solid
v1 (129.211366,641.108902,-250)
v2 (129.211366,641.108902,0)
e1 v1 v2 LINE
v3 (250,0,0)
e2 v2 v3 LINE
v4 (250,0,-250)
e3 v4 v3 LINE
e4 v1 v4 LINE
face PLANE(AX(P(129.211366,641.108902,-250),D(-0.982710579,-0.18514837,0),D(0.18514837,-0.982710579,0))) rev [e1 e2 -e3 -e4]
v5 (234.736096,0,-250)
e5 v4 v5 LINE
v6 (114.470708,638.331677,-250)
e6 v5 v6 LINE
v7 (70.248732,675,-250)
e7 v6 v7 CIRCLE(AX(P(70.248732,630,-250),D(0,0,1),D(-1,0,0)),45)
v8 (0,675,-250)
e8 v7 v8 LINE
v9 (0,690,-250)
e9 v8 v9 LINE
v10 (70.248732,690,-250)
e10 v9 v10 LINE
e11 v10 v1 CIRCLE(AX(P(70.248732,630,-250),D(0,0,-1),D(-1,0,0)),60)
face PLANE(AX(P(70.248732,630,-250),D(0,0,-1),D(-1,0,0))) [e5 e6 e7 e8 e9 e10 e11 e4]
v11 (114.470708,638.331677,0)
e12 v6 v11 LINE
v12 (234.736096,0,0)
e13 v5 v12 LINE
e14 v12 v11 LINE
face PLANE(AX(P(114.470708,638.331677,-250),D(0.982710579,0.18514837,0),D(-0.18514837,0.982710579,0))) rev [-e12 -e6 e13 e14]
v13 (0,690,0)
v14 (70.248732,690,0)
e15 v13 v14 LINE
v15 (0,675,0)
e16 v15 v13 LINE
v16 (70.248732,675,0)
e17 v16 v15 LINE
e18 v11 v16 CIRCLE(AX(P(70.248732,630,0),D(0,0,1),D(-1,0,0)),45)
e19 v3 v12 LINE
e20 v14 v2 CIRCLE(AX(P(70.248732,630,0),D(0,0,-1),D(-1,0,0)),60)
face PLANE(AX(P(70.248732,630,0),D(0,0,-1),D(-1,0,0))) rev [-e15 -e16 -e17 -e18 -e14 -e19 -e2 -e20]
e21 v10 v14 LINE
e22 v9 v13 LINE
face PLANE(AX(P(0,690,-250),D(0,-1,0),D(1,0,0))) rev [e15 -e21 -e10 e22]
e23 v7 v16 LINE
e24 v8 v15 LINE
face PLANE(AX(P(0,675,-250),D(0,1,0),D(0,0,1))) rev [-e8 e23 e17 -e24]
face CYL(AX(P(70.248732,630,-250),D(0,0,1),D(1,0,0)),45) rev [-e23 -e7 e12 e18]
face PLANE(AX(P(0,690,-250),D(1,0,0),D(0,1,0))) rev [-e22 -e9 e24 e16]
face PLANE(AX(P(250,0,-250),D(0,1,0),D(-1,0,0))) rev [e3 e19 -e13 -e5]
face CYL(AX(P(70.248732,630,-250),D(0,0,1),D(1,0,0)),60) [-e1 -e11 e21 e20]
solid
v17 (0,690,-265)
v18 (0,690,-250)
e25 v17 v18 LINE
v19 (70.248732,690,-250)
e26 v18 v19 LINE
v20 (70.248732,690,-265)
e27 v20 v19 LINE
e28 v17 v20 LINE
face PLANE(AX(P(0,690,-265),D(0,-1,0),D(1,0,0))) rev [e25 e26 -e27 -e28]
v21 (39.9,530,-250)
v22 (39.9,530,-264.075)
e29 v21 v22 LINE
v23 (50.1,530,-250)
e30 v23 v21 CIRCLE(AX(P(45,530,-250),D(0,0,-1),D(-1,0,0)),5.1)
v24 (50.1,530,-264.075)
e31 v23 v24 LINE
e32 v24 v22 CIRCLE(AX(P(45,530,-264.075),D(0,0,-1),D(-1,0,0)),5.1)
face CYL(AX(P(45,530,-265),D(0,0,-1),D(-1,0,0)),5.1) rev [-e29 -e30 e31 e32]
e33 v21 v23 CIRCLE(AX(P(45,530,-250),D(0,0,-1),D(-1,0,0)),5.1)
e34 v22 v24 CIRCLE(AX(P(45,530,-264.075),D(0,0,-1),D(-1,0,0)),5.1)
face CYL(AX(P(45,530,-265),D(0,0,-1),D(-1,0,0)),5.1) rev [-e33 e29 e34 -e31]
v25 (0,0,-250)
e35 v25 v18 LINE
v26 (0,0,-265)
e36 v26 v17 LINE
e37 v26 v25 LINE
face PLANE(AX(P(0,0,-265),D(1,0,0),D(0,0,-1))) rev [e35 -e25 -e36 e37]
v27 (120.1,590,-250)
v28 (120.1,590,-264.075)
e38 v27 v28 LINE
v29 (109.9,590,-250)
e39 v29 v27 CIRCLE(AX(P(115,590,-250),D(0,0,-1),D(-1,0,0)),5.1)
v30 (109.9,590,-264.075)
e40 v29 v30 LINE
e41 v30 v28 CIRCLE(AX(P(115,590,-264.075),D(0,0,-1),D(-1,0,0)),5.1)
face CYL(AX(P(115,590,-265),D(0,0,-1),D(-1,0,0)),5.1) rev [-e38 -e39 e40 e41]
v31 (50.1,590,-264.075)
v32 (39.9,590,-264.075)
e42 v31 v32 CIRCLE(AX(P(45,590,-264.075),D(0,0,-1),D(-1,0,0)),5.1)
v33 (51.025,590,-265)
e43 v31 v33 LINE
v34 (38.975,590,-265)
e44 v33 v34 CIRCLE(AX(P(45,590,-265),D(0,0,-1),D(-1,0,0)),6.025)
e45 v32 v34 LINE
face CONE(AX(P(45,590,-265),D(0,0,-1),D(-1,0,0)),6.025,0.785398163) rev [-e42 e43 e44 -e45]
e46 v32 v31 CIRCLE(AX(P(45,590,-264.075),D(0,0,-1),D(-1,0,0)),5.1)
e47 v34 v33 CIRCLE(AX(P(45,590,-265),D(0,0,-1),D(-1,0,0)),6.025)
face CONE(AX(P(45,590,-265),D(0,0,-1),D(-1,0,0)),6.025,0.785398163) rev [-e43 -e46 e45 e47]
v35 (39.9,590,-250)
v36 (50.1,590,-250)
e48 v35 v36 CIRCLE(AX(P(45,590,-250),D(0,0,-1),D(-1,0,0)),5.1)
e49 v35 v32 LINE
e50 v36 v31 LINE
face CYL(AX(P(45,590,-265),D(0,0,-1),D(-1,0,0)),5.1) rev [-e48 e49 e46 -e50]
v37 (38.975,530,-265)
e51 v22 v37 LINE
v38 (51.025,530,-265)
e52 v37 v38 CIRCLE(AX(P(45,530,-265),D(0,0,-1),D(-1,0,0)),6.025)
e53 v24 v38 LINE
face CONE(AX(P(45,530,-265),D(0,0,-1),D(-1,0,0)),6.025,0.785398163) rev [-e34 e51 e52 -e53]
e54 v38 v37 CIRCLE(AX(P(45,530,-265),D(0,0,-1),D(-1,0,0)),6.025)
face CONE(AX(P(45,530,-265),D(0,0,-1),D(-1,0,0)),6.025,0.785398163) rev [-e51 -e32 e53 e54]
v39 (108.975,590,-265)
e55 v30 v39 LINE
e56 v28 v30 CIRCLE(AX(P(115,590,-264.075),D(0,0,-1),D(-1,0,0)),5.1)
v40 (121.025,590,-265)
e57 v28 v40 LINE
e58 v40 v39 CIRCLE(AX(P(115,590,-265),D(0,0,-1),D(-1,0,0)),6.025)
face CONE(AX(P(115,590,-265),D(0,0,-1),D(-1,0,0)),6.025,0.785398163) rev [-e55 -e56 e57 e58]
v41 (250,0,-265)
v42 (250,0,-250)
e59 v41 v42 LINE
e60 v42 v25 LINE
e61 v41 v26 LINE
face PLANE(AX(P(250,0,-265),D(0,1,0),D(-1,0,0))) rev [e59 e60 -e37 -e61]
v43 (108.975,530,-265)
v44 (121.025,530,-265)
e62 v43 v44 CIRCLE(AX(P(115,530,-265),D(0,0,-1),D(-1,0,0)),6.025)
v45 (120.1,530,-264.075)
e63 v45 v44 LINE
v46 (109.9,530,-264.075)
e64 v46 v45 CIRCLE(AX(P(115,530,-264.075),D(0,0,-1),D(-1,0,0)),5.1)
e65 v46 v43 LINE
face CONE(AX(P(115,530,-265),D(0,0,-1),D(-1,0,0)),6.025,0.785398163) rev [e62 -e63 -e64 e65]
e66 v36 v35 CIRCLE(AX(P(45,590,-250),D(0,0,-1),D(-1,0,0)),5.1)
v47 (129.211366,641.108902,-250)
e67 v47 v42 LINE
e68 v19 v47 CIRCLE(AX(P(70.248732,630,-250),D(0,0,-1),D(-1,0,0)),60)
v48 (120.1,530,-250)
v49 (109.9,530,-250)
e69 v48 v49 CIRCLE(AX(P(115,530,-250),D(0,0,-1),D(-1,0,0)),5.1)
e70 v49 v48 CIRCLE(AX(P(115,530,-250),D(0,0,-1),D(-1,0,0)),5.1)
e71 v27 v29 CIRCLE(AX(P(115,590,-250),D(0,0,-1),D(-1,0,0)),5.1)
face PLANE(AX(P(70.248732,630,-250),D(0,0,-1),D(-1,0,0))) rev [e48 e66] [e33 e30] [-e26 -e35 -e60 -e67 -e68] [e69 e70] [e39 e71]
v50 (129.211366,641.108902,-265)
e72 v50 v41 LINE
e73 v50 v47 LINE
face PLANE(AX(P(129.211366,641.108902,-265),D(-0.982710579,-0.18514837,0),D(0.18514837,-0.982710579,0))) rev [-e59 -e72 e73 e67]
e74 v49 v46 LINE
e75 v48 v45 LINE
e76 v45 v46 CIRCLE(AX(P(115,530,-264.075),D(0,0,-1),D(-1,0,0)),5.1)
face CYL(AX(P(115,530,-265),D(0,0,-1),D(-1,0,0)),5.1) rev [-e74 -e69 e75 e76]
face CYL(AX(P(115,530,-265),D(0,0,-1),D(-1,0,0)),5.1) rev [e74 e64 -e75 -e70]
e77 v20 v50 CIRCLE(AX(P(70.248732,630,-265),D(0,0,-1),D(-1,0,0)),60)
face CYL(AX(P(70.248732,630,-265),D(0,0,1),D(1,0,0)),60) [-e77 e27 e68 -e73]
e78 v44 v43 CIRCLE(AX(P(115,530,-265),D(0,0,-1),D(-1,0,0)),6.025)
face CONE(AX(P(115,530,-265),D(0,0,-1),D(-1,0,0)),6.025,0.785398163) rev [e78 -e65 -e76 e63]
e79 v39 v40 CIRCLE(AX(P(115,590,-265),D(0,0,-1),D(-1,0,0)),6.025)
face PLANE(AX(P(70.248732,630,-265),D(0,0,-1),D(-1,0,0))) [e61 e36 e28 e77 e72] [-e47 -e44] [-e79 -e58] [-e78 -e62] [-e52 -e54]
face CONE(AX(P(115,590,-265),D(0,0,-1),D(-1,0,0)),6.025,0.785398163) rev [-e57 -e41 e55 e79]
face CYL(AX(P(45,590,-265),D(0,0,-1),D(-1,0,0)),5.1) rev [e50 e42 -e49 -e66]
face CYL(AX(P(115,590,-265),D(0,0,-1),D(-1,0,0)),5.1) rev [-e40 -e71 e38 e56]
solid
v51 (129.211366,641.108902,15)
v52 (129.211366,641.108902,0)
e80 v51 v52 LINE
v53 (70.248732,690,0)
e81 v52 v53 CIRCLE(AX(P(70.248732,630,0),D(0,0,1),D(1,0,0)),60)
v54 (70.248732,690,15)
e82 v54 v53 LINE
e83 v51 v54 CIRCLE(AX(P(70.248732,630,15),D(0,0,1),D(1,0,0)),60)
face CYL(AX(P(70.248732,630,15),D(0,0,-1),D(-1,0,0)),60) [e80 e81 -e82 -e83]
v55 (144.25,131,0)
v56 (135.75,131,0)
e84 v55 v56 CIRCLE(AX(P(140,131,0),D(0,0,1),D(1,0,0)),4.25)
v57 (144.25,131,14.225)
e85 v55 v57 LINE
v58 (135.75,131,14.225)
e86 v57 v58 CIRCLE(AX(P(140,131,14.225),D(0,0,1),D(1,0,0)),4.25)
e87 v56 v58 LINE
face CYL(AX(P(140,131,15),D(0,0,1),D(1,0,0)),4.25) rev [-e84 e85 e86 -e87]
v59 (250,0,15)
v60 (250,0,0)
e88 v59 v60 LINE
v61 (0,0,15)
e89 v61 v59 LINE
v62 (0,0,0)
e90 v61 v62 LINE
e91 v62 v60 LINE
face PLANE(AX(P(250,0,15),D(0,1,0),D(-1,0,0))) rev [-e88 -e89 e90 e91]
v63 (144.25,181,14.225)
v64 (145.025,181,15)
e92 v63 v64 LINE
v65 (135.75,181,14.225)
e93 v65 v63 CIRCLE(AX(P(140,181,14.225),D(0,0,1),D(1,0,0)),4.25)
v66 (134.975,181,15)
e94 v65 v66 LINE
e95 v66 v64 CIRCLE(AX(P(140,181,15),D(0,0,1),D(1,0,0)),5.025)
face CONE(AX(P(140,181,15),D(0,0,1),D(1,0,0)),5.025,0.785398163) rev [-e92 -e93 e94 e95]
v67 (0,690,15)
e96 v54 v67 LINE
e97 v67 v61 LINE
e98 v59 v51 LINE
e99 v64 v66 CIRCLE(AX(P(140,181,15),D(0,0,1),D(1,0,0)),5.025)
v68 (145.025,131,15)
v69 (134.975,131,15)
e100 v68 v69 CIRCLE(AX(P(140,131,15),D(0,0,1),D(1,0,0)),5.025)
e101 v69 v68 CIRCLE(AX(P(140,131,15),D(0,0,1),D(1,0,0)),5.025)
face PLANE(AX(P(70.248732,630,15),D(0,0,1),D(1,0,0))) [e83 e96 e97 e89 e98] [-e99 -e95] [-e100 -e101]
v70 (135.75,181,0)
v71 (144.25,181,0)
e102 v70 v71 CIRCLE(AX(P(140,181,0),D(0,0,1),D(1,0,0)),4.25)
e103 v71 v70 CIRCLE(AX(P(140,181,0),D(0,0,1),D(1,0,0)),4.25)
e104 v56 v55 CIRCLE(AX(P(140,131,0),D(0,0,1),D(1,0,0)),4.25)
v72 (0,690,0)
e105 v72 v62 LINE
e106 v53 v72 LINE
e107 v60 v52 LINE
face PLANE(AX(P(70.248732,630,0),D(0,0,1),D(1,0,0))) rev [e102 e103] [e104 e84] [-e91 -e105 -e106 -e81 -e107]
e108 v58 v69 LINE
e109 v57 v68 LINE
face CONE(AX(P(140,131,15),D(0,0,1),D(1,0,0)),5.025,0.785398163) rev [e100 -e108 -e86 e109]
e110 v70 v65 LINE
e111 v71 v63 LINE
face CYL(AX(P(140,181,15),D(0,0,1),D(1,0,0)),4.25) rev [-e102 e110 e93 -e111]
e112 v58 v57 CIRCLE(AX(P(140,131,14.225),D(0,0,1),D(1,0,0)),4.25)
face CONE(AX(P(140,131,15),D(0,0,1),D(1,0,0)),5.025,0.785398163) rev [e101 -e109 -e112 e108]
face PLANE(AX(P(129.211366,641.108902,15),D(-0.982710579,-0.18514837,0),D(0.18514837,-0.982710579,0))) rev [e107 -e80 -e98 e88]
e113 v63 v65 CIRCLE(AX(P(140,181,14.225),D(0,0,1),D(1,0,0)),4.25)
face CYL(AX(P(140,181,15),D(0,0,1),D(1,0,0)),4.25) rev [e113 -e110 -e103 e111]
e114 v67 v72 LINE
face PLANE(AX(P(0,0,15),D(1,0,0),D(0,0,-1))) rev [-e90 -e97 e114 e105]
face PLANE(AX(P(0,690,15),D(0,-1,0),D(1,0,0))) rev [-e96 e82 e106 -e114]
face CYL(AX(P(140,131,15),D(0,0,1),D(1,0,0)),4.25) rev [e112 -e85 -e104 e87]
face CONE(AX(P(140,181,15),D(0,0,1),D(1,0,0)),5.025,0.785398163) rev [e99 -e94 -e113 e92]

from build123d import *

# Parameters (mm, degrees)
EXTRUDE_1_DEPTH              = 15
EXTRUDE_2_DEPTH              = 250
EXTRUDE_3_DEPTH              = 15
HOLE_WIZARD_M10_1_AT_2_COUNT = 2
HOLE_WIZARD_M10_1_AT_2_PITCH = 50
HOLE_WIZARD_M12_1_AT_2_COUNT = 2
HOLE_WIZARD_M12_1_AT_2_PITCH = 70
HOLE_WIZARD_M12_1_AT_3_COUNT = 2
HOLE_WIZARD_M12_1_AT_3_PITCH = 92.195444573
HOLE_WIZARD_M12_1_AT_4_COUNT = 2
HOLE_WIZARD_M12_1_AT_4_PITCH = 60


with BuildPart() as part:
    # 草图1 → 凸台-拉伸1 (new body)
    with BuildSketch(Plane.XY):
        with BuildLine():
            Line((0, 0), (0, 690))
            Line((0, 690), (70.248731542, 690))
            ThreePointArc((70.248731542, 690), (108.546681021, 676.187304162), (129.211366254, 641.108902192))
            Line((129.211366254, 641.108902192), (250, 0))
            Line((250, 0), (0, 0))
        make_face()
    extrude(amount=EXTRUDE_1_DEPTH)

    # 草图5 → M10 螺纹孔1 (revolve, cut)
    with BuildSketch(Plane(origin=(140, 181, 15), x_dir=(0, -1, 0), z_dir=(1, 0, 0))):
        Polygon((0, 0), (0, 15), (4.25, 15), (4.25, 0.775), (5.025, 0), align=None)
    hole_wizard_m10_1 = revolve(axis=Axis((140, 181, 21.35), (0, 0, -1)), mode=Mode.SUBTRACT)

    # M10 螺纹孔1 at 2: M10 螺纹孔1 ×2
    with Locations(*[(0, -i * HOLE_WIZARD_M10_1_AT_2_PITCH, 0) for i in range(1, HOLE_WIZARD_M10_1_AT_2_COUNT)]):
        add(hole_wizard_m10_1, mode=Mode.SUBTRACT)


with BuildPart() as body_2:
    # 草图2 → 凸台-拉伸2 (new body)
    with BuildSketch(Plane(origin=(0, 0, 0), x_dir=(-1, 0, 0), z_dir=(0, 0, -1))):
        with BuildLine():
            Line((0, 675), (-70.248731542, 675))
            ThreePointArc((-70.248731542, 675), (-98.972193651, 664.640478122), (-114.470707576, 638.331676644))
            Line((-114.470707576, 638.331676644), (-234.736095929, 0))
            Line((-234.736095929, 0), (-250, 0))
            Line((-250, 0), (-129.211366254, 641.108902192))
            ThreePointArc((-129.211366254, 641.108902192), (-108.546681021, 676.187304162), (-70.248731542, 690))
            Line((-70.248731542, 690), (0, 690))
            Line((0, 690), (0, 675))
        make_face()
    extrude(amount=EXTRUDE_2_DEPTH)


with BuildPart() as body_3:
    # 草图3 → 凸台-拉伸3 (new body)
    with BuildSketch(Plane(origin=(0, 0, -250), x_dir=(-1, 0, 0), z_dir=(0, 0, -1))):
        with BuildLine():
            Line((-250, 0), (0, 0))
            Line((0, 0), (0, 690))
            Line((0, 690), (-70.248731542, 690))
            ThreePointArc((-70.248731542, 690), (-108.546681021, 676.187304162), (-129.211366254, 641.108902192))
            Line((-129.211366254, 641.108902192), (-250, 0))
        make_face()
    extrude(amount=EXTRUDE_3_DEPTH)

    # 草图7 → M12 螺纹孔1 (revolve, cut)
    with BuildSketch(Plane(origin=(45, 590, -265), x_dir=(0, 1, 0), z_dir=(1, 0, 0))):
        Polygon((0, 0), (0, 15.001), (5.1, 15.001), (5.1, 0.925), (6.025, 0), align=None)
    hole_wizard_m12_1 = revolve(axis=Axis((45, 590, -271.35), (0, 0, 1)), mode=Mode.SUBTRACT)

    # M12 螺纹孔1 at 2: M12 螺纹孔1 ×2
    with Locations(*[(i * HOLE_WIZARD_M12_1_AT_2_PITCH, 0, 0) for i in range(1, HOLE_WIZARD_M12_1_AT_2_COUNT)]):
        add(hole_wizard_m12_1, mode=Mode.SUBTRACT)

    # M12 螺纹孔1 at 3: M12 螺纹孔1 ×2
    with Locations(*[Vector(0.7592566023652966, -0.6507913734559686, 0) * (i * HOLE_WIZARD_M12_1_AT_3_PITCH) for i in range(1, HOLE_WIZARD_M12_1_AT_3_COUNT)]):
        add(hole_wizard_m12_1, mode=Mode.SUBTRACT)

    # M12 螺纹孔1 at 4: M12 螺纹孔1 ×2
    with Locations(*[(0, -i * HOLE_WIZARD_M12_1_AT_4_PITCH, 0) for i in range(1, HOLE_WIZARD_M12_1_AT_4_COUNT)]):
        add(hole_wizard_m12_1, mode=Mode.SUBTRACT)


solid = Compound([part.part, body_2.part, body_3.part])
